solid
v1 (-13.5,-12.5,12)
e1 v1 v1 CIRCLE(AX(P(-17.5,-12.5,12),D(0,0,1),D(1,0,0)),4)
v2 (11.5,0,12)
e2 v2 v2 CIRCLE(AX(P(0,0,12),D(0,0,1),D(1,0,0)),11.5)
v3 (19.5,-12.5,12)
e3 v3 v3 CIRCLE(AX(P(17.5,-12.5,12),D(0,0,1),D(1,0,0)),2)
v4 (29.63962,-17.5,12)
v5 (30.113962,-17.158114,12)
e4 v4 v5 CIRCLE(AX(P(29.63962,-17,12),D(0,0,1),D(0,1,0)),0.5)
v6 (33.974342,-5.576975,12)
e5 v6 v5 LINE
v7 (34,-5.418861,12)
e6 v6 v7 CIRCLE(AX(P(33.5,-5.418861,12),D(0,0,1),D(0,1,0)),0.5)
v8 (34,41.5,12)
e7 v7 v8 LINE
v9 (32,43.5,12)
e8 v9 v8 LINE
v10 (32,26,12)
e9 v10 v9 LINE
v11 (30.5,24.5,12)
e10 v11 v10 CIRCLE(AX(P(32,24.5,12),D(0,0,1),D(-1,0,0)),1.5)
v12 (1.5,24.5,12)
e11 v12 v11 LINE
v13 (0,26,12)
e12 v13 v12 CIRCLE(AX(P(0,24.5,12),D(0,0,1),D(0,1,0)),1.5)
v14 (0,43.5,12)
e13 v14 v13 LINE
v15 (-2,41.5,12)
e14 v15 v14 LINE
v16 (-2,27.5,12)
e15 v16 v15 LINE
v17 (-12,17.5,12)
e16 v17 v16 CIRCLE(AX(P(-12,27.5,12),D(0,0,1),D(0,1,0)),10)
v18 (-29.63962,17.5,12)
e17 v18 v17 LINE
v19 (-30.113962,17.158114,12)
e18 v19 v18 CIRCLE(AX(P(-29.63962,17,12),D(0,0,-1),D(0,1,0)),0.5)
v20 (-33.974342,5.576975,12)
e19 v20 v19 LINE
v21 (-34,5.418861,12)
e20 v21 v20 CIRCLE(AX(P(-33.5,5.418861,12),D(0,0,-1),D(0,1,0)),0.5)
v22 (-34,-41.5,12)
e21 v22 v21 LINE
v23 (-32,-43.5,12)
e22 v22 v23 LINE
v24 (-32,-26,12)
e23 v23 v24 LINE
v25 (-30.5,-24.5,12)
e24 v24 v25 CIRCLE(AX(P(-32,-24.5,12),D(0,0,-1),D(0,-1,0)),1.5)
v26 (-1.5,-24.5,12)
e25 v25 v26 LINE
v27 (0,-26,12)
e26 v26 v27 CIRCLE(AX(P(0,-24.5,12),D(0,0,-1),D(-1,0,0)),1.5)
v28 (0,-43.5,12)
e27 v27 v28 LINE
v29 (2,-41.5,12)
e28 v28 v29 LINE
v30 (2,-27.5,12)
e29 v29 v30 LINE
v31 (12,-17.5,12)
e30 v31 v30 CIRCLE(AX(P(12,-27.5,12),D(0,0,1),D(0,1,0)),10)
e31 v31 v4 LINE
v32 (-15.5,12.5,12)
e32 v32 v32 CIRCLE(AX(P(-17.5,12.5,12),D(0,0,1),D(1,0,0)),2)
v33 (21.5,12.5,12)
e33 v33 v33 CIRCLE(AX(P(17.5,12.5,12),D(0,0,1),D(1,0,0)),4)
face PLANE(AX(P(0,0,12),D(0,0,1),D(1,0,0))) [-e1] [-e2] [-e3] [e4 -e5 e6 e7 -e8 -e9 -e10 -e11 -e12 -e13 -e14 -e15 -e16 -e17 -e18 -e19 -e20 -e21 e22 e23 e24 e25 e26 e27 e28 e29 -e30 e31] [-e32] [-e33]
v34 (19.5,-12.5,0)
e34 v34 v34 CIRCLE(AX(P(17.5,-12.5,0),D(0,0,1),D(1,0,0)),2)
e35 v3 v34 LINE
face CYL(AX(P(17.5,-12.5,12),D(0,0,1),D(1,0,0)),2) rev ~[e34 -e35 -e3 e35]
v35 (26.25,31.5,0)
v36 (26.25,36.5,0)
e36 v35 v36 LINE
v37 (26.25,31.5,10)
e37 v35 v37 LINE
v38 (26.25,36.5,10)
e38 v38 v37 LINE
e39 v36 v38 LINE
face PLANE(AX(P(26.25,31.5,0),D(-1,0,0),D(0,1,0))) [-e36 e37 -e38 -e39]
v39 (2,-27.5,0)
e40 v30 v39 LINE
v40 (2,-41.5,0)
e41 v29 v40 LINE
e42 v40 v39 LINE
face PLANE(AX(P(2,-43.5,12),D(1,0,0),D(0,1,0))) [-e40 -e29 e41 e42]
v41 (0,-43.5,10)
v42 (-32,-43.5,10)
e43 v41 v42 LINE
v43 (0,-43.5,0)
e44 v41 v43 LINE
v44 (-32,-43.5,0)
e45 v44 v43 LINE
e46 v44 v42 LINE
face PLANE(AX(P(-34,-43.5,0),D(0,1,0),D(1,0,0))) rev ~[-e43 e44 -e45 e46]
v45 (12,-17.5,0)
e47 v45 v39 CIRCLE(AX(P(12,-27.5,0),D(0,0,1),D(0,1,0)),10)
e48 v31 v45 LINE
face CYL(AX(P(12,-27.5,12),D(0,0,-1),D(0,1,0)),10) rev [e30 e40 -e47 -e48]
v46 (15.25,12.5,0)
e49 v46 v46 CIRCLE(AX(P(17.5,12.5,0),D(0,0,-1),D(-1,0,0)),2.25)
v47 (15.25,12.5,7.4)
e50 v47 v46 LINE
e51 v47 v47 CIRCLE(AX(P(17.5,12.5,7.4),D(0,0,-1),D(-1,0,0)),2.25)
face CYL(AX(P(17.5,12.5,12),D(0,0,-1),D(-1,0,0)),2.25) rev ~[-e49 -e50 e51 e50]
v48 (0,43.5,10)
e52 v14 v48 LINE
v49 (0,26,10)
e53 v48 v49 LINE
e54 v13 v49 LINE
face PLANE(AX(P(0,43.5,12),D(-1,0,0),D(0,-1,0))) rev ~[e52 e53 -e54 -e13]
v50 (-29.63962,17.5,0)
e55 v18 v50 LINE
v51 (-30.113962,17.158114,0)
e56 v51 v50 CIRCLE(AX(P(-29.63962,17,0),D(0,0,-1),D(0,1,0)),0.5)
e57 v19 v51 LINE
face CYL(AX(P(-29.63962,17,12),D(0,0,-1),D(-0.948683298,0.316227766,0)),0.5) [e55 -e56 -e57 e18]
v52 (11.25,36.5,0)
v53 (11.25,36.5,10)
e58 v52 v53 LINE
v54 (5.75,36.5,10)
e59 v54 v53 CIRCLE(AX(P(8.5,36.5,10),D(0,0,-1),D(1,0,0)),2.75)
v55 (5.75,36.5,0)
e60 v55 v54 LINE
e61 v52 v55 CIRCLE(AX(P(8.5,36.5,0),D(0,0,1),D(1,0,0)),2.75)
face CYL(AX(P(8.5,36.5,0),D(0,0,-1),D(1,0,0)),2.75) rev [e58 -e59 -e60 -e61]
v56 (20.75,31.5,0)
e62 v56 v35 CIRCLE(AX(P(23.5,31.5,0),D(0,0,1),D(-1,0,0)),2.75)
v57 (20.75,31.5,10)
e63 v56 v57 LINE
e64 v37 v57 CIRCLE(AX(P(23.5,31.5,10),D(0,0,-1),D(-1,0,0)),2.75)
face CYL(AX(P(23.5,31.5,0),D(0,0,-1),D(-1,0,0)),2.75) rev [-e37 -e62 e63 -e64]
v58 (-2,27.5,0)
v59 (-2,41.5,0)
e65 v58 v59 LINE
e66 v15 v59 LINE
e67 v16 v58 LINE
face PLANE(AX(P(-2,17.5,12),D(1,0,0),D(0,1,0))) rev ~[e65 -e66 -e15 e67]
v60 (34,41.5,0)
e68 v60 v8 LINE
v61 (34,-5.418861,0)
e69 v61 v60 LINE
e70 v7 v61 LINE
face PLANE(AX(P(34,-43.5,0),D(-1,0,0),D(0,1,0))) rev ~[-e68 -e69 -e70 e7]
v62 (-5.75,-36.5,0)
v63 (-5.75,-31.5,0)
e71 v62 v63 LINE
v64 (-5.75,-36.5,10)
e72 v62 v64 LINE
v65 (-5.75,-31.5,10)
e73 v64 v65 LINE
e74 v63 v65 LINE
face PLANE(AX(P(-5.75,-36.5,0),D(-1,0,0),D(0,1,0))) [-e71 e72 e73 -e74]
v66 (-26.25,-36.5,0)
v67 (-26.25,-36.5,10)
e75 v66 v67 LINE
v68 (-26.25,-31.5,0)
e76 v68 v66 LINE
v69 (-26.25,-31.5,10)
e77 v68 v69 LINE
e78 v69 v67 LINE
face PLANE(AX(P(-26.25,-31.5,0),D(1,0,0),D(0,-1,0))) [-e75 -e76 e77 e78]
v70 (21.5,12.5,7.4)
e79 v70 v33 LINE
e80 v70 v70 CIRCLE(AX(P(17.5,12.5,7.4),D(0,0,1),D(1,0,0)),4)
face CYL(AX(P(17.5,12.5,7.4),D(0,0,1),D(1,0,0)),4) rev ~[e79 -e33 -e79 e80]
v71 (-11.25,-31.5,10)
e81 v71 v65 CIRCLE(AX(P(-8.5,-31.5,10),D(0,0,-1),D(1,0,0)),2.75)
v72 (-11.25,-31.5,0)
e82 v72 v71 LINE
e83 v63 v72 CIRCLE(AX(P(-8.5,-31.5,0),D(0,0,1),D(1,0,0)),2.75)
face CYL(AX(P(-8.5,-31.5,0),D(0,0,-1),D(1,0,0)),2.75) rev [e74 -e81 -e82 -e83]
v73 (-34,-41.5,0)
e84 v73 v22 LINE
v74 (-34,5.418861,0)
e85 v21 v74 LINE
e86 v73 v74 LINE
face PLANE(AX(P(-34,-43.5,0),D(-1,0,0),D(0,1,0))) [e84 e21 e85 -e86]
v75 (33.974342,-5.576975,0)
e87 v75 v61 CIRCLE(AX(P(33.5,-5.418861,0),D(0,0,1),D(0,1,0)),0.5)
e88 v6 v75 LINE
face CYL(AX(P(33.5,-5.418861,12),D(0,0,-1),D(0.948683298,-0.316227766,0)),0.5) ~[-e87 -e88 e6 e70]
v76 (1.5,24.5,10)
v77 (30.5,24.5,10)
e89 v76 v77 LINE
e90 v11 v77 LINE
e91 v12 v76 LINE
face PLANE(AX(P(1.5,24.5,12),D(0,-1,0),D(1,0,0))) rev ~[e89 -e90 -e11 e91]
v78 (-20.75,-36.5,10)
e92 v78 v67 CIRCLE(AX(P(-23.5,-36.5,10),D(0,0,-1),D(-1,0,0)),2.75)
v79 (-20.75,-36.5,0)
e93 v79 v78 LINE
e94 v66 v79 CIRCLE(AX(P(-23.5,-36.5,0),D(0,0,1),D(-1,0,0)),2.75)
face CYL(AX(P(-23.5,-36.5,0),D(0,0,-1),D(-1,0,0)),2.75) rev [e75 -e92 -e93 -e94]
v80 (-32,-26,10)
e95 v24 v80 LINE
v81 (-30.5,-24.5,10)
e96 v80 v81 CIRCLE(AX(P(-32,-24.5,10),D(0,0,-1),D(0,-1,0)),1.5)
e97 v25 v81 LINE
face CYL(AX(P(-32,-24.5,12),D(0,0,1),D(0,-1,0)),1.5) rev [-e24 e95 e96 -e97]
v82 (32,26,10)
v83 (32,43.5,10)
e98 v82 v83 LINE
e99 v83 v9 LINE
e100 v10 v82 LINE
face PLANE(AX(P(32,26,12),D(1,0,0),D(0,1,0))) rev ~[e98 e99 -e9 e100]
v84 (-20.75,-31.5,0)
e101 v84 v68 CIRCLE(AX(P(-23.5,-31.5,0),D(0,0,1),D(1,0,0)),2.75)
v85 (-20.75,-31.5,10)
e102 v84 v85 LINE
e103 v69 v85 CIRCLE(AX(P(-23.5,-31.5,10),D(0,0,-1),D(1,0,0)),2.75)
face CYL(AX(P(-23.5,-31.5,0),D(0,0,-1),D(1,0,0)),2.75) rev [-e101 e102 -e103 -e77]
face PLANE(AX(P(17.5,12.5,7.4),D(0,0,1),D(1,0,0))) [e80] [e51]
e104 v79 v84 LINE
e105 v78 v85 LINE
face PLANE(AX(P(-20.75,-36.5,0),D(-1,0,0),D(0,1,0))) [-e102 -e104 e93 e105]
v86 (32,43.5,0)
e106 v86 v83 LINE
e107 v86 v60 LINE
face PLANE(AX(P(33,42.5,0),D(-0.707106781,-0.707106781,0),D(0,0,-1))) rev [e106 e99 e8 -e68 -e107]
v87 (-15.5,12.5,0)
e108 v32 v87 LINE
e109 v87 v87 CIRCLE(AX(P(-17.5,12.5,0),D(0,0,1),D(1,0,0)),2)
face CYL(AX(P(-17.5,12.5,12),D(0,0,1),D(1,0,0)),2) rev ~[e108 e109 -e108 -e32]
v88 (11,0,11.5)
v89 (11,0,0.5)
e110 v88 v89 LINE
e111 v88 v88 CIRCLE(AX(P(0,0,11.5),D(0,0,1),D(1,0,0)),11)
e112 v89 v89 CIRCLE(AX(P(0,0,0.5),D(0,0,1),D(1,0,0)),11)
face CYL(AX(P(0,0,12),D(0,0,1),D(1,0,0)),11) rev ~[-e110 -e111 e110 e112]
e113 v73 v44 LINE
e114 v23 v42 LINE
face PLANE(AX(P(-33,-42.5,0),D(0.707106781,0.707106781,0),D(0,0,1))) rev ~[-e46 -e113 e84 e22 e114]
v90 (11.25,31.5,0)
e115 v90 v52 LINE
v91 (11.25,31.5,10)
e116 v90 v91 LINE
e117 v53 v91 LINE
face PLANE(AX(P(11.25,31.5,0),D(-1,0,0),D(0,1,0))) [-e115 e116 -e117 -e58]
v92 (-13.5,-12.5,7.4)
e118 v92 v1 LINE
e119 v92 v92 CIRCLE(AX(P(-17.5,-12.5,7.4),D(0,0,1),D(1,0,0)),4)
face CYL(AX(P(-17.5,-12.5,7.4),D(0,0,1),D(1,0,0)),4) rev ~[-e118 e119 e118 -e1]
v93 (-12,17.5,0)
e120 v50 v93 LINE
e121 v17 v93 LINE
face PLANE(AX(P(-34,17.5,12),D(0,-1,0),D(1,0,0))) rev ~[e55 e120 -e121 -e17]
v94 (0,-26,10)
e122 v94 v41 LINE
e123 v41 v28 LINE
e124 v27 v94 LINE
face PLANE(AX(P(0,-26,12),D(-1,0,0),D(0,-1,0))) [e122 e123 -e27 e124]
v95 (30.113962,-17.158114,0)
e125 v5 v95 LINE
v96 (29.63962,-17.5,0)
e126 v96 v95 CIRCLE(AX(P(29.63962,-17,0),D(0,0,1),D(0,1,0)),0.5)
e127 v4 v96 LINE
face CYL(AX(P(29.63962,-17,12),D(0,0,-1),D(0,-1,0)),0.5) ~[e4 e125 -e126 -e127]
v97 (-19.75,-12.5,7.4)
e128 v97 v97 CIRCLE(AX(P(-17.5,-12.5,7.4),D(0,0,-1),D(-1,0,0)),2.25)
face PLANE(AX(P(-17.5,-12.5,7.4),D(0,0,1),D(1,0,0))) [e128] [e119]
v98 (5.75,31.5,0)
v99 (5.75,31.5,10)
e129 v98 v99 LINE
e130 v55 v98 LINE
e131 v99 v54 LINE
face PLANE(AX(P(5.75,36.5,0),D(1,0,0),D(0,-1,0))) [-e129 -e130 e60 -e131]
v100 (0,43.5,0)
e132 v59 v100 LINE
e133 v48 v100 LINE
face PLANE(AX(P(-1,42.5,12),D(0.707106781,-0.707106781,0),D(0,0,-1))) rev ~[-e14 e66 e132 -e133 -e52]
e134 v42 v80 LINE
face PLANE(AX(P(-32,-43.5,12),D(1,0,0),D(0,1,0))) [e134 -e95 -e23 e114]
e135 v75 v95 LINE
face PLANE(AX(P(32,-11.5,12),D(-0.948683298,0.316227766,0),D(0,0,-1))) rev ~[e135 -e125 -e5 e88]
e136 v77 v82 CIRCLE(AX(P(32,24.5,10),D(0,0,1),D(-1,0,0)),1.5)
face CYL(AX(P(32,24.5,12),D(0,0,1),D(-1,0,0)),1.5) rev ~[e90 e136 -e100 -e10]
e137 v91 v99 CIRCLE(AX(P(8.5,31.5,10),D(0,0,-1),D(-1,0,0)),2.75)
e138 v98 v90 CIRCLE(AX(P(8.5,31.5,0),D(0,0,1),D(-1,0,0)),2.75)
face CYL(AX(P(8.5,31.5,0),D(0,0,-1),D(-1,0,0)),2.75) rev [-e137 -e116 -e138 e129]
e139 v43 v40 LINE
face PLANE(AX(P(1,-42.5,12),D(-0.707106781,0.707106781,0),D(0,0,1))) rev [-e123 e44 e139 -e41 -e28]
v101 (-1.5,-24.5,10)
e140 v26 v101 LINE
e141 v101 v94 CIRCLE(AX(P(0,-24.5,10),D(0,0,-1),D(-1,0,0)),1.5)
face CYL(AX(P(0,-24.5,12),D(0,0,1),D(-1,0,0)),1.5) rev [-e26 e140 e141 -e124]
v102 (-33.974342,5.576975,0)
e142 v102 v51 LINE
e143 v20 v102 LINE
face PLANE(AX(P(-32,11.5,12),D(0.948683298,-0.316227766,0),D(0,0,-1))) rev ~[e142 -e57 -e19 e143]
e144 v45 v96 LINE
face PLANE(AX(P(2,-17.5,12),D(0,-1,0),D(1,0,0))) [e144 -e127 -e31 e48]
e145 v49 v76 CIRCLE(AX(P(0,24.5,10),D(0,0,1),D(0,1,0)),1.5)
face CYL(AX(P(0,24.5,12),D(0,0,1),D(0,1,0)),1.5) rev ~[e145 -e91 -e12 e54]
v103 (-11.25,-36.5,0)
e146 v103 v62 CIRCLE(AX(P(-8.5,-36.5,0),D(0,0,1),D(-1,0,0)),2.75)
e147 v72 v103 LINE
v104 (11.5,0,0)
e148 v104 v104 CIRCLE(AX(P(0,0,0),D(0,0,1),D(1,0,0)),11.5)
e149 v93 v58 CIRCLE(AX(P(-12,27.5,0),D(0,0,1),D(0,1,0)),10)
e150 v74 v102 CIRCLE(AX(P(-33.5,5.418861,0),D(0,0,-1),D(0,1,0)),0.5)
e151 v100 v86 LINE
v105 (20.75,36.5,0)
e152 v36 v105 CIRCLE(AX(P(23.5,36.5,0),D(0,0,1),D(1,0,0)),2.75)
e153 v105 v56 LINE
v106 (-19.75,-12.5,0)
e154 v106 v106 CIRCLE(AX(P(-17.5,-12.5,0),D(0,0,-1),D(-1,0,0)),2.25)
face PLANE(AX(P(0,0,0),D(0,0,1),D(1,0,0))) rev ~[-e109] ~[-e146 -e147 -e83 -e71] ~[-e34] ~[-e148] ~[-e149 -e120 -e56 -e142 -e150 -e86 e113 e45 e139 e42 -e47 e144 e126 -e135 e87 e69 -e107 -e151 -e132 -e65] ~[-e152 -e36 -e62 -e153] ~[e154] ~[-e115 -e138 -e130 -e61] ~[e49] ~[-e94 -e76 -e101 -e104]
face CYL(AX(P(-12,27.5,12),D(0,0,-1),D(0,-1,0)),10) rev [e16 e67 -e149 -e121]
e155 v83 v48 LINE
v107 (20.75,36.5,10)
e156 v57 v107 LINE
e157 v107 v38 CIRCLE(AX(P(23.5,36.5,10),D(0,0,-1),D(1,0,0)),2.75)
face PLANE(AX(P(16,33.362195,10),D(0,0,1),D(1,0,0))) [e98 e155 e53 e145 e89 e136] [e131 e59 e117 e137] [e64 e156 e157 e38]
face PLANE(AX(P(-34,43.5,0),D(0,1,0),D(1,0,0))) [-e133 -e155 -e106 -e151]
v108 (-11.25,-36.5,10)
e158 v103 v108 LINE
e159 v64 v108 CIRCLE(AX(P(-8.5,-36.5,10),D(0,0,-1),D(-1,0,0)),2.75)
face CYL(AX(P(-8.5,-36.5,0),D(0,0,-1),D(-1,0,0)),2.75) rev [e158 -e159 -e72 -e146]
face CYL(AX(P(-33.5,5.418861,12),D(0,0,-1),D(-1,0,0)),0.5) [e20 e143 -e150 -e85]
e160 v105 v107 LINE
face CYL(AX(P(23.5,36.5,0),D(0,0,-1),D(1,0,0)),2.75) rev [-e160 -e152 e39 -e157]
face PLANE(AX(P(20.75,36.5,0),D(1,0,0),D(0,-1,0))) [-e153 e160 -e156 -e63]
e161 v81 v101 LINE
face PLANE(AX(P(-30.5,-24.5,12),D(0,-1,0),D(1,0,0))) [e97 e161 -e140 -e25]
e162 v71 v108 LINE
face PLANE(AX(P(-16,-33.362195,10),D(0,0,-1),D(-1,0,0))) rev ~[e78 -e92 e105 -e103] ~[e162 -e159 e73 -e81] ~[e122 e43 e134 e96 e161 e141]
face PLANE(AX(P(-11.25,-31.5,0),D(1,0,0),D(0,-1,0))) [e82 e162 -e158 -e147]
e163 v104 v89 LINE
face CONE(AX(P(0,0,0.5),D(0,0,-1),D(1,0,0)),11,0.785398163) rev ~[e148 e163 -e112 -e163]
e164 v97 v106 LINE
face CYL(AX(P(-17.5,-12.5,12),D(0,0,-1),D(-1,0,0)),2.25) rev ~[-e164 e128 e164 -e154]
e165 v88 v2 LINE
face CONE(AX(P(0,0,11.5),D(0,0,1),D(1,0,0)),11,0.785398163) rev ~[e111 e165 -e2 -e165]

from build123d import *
from OCP.BRepFilletAPI import BRepFilletAPI_MakeChamfer

# Parameters (mm, degrees)
SKETCH1_W                                            = 68
SKETCH1_H                                            = 87
BOSS_EXTRUDE1_DEPTH                                  = 12
SKETCH3_R                                            = 11
SKETCH3_W                                            = 32
SKETCH3_H                                            = 26
CUT_EXTRUDE2_DEPTH                                   = 57.5
CUT_EXTRUDE5_DEPTH                                   = 2
FILLET1_R                                            = 10
CHAMFER1_SIZE                                        = 2
CUT_EXTRUDE6_DEPTH                                   = 57.5
CHAMFER2_SIZE                                        = 12
CHAMFER2_SIZE2                                       = 4
FILLET3_R                                            = 0.5
HOLE_SIZE_BY_SOCKET_HEAD_CAP_SCREW_TYPE1_D           = 4.5
HOLE_SIZE_BY_SOCKET_HEAD_CAP_SCREW_TYPE1_CBORE_D     = 8
HOLE_SIZE_BY_SOCKET_HEAD_CAP_SCREW_TYPE1_CBORE_DEPTH = 4.6
SKETCH15_R                                           = 2
CUT_EXTRUDE4_DEPTH                                   = 25
CHAMFER3_SIZE                                        = 0.5


with BuildPart() as part:
    # Sketch1 → Boss-Extrude1 (new body)
    with BuildSketch(Plane.XY):
        Rectangle(SKETCH1_W, SKETCH1_H)
    extrude(amount=BOSS_EXTRUDE1_DEPTH)

    # Sketch3 → Cut-Extrude2 (cut, through all)
    with BuildSketch(Plane.XY.offset(12)):
        Circle(SKETCH3_R)
        with Locations((-18, 30.5)):
            Rectangle(SKETCH3_W, SKETCH3_H)
        with Locations((18, -30.5)):
            Rectangle(SKETCH3_W, SKETCH3_H)
    extrude(amount=-CUT_EXTRUDE2_DEPTH, mode=Mode.SUBTRACT)

    # Sketch16 → Cut-Extrude5 (cut)
    with BuildSketch(Plane.XY.offset(12)):
        with BuildLine():
            Line((0, -43.5), (-32, -43.5))
            Line((-32, -43.5), (-32, -26))
            ThreePointArc((-32, -26), (-33.060660172, -23.439339828), (-30.5, -24.5))
            Line((-30.5, -24.5), (-1.5, -24.5))
            ThreePointArc((-1.5, -24.5), (1.060660172, -23.439339828), (0, -26))
            Line((0, -26), (0, -43.5))
        make_face()
        with BuildLine():
            Line((32, 43.5), (0, 43.5))
            Line((0, 43.5), (0, 26))
            ThreePointArc((0, 26), (-1.060660172, 23.439339828), (1.5, 24.5))
            Line((1.5, 24.5), (30.5, 24.5))
            ThreePointArc((30.5, 24.5), (33.060660172, 23.439339828), (32, 26))
            Line((32, 26), (32, 43.5))
        make_face()
    extrude(amount=-CUT_EXTRUDE5_DEPTH, mode=Mode.SUBTRACT)

    # Fillet1
    fillet1_edges = [part.edges().sort_by_distance(p)[0] for p in [
        (-2, 17.5, 6),
        (2, -17.5, 6),
    ]]
    fillet(fillet1_edges, radius=FILLET1_R)

    # Chamfer1
    chamfer1_edges = [part.edges().sort_by_distance(p)[0] for p in [
        (-34, -43.5, 6),
        (2, -43.5, 6),
        (34, 43.5, 6),
        (-2, 43.5, 6),
    ]]
    chamfer(chamfer1_edges, length=CHAMFER1_SIZE)

    # Sketch17 → Cut-Extrude6 (cut, through all)
    with BuildSketch(Plane(origin=(0, 0, 0), x_dir=(-1, 0, 0), z_dir=(0, 0, -1))):
        with BuildLine():
            Line((-20.75, 36.5), (-20.75, 31.5))
            ThreePointArc((-20.75, 31.5), (-23.5, 28.75), (-26.25, 31.5))
            Line((-26.25, 31.5), (-26.25, 36.5))
            ThreePointArc((-26.25, 36.5), (-23.5, 39.25), (-20.75, 36.5))
        make_face()
        with BuildLine():
            Line((-5.75, 36.5), (-5.75, 31.5))
            ThreePointArc((-5.75, 31.5), (-8.5, 28.75), (-11.25, 31.5))
            Line((-11.25, 31.5), (-11.25, 36.5))
            ThreePointArc((-11.25, 36.5), (-8.5, 39.25), (-5.75, 36.5))
        make_face()
        with BuildLine():
            Line((26.25, -31.5), (26.25, -36.5))
            ThreePointArc((26.25, -36.5), (23.5, -39.25), (20.75, -36.5))
            Line((20.75, -36.5), (20.75, -31.5))
            ThreePointArc((20.75, -31.5), (23.5, -28.75), (26.25, -31.5))
        make_face()
        with BuildLine():
            Line((11.25, -31.5), (11.25, -36.5))
            ThreePointArc((11.25, -36.5), (8.5, -39.25), (5.75, -36.5))
            Line((5.75, -36.5), (5.75, -31.5))
            ThreePointArc((5.75, -31.5), (8.5, -28.75), (11.25, -31.5))
        make_face()
    extrude(amount=-CUT_EXTRUDE6_DEPTH, mode=Mode.SUBTRACT)

    # Chamfer2: one chamfer whose edges measure the first distance from different faces: ONE call of the kernel's chamfer builder (chamfer() names one face for all edges)
    chamfer2_edges_1 = [part.edges().sort_by_distance(p)[0] for p in [
        (-34, 17.5, 6),
    ]]
    chamfer2_side_1 = [part.faces().sort_by_distance(p)[0] for p in [
        (-34, -12, 6),
    ]]
    chamfer2_edges_2 = [part.edges().sort_by_distance(p)[0] for p in [
        (34, -17.5, 6),
    ]]
    chamfer2_side_2 = [part.faces().sort_by_distance(p)[0] for p in [
        (34, 12, 6),
    ]]
    chamfer2 = BRepFilletAPI_MakeChamfer(part.part.solid().wrapped)
    for e in chamfer2_edges_1:
        chamfer2.Add(CHAMFER2_SIZE, CHAMFER2_SIZE2, e.wrapped, chamfer2_side_1[0].wrapped)  # the first distance lies on this face
    for e in chamfer2_edges_2:
        chamfer2.Add(CHAMFER2_SIZE, CHAMFER2_SIZE2, e.wrapped, chamfer2_side_2[0].wrapped)  # the first distance lies on this face
    add(Compound.cast(chamfer2.Shape()), mode=Mode.REPLACE)

    # Fillet3
    fillet3_edges = [part.edges().sort_by_distance(p)[0] for p in [
        (30, -17.5, 6),
        (34, -5.5, 6),
        (-30, 17.5, 6),
        (-34, 5.5, 6),
    ]]
    fillet(fillet3_edges, radius=FILLET3_R)

    # Hole size by socket head cap screw type1 (through all)
    with Locations(Plane.XY.offset(12)):
        with Locations((17.5, 12.5), (-17.5, -12.5)):
            CounterBoreHole(HOLE_SIZE_BY_SOCKET_HEAD_CAP_SCREW_TYPE1_D / 2, HOLE_SIZE_BY_SOCKET_HEAD_CAP_SCREW_TYPE1_CBORE_D / 2, HOLE_SIZE_BY_SOCKET_HEAD_CAP_SCREW_TYPE1_CBORE_DEPTH)

    # Sketch15 → Cut-Extrude4 (cut)
    with BuildSketch(Plane.XY.offset(12)):
        with Locations((17.5, -12.5)):
            Circle(SKETCH15_R)
        with Locations((-17.5, 12.5)):
            Circle(SKETCH15_R)
    extrude(amount=-CUT_EXTRUDE4_DEPTH, mode=Mode.SUBTRACT)

    # Chamfer3
    chamfer3_edges = [part.edges().sort_by_distance(p)[0] for p in [
        (-11, 0, 0),
        (-11, 0, 12),
    ]]
    chamfer(chamfer3_edges, length=CHAMFER3_SIZE)


solid = part.part
